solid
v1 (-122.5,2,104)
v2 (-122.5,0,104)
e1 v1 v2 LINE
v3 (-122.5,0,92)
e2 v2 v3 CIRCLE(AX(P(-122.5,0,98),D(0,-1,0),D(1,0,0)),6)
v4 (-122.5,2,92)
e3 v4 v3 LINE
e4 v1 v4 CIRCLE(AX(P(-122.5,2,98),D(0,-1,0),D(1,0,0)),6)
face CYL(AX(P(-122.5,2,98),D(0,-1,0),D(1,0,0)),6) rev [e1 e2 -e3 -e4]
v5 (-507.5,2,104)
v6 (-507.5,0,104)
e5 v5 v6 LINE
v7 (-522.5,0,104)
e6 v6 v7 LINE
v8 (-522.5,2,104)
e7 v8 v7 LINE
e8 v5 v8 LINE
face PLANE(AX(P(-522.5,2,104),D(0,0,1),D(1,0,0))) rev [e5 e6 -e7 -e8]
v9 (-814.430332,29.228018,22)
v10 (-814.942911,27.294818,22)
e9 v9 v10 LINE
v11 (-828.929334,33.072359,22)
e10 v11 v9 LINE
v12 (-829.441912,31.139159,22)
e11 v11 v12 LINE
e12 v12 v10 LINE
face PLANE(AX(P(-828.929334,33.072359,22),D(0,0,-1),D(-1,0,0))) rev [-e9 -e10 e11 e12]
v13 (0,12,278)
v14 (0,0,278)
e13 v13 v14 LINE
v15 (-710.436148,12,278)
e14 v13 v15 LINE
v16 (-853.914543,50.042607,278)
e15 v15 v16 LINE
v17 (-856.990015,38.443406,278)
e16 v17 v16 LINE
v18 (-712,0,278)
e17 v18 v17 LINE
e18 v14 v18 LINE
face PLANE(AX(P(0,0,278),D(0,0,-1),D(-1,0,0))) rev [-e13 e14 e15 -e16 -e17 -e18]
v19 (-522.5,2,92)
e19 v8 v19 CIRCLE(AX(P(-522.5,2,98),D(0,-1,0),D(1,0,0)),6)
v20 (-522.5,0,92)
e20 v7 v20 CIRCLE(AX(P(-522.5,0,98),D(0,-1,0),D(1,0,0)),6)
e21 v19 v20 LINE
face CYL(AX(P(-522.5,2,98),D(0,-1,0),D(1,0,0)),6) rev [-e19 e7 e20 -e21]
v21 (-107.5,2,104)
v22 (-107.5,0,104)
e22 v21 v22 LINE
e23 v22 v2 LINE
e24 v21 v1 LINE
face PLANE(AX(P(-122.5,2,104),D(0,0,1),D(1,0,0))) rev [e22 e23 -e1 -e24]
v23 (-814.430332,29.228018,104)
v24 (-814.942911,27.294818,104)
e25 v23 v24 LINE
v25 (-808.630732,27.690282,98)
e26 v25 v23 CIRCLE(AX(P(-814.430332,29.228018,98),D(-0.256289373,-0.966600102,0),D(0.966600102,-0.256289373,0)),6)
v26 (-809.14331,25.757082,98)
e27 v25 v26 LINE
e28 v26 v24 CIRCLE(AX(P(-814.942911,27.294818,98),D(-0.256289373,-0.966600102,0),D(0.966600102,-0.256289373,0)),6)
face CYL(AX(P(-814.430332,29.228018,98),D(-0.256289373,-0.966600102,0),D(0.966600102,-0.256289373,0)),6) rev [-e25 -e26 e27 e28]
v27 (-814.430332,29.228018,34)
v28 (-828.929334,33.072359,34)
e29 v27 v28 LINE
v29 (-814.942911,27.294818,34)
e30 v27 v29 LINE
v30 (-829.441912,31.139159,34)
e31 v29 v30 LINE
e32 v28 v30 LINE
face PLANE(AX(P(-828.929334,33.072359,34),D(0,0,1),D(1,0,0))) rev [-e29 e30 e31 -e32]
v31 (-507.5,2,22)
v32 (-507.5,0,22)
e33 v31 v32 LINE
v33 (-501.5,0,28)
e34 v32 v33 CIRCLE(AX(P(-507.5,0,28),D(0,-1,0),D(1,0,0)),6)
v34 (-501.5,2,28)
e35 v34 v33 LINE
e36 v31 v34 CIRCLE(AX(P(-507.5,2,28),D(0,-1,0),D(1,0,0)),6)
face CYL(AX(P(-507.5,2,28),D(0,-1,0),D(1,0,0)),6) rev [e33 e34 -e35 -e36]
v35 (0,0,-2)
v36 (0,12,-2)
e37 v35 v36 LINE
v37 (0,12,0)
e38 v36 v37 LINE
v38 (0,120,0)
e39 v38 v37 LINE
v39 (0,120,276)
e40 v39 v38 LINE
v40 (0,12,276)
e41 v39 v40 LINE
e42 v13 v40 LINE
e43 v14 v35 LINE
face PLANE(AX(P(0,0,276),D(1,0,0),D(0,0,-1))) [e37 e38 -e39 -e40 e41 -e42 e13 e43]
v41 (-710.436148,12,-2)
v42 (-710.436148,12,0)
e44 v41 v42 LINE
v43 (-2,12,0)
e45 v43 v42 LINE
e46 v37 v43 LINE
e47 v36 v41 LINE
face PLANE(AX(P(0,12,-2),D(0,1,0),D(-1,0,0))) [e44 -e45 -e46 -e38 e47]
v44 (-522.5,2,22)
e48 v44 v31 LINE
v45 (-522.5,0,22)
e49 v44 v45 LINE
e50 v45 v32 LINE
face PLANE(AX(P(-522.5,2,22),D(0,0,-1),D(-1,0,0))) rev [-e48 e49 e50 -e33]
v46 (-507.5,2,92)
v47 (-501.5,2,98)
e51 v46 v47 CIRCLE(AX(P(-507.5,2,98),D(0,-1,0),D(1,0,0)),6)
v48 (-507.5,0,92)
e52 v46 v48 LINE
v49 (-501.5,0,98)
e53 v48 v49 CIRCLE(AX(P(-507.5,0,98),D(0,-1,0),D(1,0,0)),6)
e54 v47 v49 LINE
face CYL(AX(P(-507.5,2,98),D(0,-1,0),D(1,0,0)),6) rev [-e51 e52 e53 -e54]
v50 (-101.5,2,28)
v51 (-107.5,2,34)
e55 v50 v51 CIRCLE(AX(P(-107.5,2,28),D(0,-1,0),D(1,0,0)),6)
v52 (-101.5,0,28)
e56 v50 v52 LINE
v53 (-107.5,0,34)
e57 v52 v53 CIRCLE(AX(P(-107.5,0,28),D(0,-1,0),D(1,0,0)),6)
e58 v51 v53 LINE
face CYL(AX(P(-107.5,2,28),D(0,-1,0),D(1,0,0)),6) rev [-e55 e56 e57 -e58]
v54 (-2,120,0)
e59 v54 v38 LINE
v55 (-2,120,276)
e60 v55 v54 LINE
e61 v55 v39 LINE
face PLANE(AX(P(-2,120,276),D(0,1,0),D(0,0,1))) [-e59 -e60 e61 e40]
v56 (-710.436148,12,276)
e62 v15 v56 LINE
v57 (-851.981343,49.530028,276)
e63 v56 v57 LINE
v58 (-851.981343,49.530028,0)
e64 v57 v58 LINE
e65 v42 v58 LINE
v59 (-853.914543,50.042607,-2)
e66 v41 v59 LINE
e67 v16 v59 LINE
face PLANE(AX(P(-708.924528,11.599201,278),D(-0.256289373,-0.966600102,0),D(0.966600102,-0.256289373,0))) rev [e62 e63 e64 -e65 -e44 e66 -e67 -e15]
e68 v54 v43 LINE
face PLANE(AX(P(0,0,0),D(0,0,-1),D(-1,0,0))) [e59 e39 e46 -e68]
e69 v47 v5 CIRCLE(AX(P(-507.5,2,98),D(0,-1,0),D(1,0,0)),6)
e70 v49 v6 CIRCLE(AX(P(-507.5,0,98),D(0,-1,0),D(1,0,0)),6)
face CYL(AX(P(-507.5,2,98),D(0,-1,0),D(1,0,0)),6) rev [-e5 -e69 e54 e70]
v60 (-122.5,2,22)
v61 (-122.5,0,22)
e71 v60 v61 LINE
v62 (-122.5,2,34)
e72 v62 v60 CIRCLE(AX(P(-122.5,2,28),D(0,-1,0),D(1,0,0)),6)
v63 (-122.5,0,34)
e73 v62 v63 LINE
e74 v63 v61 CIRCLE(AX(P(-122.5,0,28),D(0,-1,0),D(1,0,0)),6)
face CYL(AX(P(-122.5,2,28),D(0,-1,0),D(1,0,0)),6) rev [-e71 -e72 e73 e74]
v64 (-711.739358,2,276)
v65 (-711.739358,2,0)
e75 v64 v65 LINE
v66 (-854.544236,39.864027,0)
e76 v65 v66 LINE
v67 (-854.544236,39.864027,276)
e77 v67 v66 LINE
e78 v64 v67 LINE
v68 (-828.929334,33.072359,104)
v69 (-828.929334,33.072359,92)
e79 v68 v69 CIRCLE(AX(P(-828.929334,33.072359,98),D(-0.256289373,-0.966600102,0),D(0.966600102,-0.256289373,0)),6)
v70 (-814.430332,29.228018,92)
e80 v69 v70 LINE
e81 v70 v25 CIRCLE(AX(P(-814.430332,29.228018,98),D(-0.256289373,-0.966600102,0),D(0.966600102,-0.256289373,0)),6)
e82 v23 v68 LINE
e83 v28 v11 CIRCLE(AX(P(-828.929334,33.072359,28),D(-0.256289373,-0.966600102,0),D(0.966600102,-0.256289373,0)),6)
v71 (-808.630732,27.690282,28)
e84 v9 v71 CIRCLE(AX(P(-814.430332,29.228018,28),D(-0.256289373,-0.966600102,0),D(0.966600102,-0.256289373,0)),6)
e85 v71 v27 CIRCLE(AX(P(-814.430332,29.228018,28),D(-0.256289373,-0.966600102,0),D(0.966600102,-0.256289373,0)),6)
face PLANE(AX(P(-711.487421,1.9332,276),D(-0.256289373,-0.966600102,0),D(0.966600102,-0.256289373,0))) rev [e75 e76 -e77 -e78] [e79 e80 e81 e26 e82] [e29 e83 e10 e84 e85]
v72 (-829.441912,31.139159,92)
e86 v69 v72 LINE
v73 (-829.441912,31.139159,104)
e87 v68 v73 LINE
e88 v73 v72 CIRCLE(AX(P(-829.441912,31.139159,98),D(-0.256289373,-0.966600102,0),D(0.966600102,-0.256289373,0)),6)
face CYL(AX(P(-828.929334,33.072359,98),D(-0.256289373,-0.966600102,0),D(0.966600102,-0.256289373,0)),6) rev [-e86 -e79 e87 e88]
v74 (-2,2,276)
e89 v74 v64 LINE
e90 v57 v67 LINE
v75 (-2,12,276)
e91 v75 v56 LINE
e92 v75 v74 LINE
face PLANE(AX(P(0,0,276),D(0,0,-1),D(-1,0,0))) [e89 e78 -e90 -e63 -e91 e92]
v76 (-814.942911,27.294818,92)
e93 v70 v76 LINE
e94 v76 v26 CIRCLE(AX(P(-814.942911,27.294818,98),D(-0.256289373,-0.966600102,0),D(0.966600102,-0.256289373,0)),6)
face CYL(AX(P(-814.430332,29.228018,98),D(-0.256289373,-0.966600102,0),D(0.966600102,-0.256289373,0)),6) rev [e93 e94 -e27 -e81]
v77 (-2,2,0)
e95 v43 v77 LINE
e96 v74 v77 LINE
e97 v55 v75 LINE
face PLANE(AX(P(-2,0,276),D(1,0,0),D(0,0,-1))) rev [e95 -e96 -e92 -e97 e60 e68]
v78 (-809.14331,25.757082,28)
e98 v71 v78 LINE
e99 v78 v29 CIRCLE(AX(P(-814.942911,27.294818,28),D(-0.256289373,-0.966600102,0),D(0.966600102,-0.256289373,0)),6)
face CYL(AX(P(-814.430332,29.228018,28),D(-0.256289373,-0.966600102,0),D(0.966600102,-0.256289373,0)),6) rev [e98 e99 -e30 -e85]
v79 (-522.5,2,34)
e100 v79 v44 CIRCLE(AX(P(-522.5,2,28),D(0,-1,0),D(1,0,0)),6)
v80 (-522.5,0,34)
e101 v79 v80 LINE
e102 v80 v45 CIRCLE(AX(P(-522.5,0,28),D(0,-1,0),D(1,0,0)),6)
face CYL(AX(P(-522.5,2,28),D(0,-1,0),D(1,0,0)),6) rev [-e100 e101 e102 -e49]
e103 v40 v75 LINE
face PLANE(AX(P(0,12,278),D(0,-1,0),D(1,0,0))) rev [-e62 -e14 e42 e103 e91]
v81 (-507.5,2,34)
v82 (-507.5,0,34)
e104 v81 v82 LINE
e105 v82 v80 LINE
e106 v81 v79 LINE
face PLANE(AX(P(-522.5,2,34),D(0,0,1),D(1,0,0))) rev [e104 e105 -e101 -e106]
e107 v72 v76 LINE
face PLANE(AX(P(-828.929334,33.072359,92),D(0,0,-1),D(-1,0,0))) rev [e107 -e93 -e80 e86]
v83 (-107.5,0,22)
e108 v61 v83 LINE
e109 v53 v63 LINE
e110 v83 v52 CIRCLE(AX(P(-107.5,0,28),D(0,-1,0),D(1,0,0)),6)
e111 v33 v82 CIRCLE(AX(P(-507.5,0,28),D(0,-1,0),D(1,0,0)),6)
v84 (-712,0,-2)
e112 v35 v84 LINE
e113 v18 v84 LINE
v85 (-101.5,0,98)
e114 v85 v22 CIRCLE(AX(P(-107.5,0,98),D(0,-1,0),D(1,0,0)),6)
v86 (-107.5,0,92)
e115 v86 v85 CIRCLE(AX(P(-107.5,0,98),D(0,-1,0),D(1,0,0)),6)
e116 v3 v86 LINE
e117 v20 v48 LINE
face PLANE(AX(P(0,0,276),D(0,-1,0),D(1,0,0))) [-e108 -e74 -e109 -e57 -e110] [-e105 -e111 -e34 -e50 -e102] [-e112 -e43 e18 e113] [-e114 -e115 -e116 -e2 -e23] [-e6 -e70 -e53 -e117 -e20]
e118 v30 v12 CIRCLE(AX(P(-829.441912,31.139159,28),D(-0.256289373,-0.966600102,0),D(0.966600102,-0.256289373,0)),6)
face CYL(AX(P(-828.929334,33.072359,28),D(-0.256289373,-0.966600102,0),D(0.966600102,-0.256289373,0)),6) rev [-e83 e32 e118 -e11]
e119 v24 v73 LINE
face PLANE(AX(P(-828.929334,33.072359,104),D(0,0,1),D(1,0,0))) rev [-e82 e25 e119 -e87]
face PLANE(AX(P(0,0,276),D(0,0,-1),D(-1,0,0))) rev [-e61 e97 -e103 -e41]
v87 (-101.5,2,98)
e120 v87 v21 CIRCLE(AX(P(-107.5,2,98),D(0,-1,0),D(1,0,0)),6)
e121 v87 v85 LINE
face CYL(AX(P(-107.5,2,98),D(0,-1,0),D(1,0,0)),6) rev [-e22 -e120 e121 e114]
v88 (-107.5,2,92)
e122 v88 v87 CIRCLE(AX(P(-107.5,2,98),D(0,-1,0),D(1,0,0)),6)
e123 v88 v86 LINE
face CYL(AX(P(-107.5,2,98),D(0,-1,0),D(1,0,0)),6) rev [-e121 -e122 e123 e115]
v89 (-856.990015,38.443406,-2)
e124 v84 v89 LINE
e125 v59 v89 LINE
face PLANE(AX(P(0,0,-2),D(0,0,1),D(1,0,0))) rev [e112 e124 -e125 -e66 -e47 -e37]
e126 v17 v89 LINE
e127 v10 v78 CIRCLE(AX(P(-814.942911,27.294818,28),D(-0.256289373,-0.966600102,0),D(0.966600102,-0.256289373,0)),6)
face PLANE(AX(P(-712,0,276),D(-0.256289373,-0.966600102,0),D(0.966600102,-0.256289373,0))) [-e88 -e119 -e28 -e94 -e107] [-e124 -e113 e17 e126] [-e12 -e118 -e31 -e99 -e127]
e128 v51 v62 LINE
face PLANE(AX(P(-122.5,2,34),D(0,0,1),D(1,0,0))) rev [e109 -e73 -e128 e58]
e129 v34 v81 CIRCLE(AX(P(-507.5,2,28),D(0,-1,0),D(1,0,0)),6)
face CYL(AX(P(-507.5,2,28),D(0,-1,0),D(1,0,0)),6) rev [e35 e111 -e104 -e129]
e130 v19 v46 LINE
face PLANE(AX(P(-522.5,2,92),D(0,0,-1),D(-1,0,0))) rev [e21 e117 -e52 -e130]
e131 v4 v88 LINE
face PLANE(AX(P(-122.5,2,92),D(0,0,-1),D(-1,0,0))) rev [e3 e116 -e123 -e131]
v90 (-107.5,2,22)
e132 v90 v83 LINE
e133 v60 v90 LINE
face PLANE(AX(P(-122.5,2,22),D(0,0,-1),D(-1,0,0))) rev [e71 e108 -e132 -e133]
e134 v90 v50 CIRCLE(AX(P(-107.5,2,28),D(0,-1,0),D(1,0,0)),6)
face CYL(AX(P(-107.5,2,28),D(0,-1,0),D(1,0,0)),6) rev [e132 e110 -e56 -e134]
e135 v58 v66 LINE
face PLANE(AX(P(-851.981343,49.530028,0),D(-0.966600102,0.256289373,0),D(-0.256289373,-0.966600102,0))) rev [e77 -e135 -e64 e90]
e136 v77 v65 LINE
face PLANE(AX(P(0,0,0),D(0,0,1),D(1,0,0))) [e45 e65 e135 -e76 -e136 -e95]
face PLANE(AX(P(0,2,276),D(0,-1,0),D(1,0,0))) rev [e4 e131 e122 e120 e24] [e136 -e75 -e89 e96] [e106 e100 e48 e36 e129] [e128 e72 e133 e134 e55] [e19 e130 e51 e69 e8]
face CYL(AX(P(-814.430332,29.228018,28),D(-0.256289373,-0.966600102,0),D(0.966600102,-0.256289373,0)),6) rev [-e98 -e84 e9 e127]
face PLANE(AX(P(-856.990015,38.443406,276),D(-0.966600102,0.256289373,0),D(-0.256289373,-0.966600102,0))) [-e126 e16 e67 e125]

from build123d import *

# Parameters (mm, degrees)
EXTRUDE_THIN1_DEPTH  = 276
EXTRUDE_THIN2_DEPTH  = 2
EXTRUDE_THIN3_DEPTH  = 2
CUT_EXTRUDE1_DEPTH   = 2
CUT_EXTRUDE2_DEPTH   = 2
SKETCH7_W            = 2
SKETCH7_H            = 276
BOSS_EXTRUDE1_DEPTH  = 10
LPATTERN1_COUNT      = 2
LPATTERN1_PITCH      = 70
LPATTERN2_COUNT      = 2
LPATTERN2_PITCH      = 70
LPATTERN2_COUNT_DIR2 = 2
LPATTERN2_PITCH_DIR2 = 400


with BuildPart() as part:
    # Sketch1 → Extrude-Thin1 (new body)
    with BuildSketch(Plane.XY):
        Polygon((-856.990015303, 38.44340597), (-712, 0), (0, 0), (0, 120), (-2, 120), (-2, 2), (-711.739357917, 2), (-856.477436556, 40.376606174), align=None)
    extrude(amount=EXTRUDE_THIN1_DEPTH)

    # Sketch2 → Extrude-Thin2 (add)
    with BuildSketch(Plane.XY.offset(276)):
        Polygon((0, 0), (-712, 0), (-856.990015303, 38.44340597), (-853.914542825, 50.042607194), (-710.436147504, 12), (0, 12), align=None)
    extrude(amount=EXTRUDE_THIN2_DEPTH)

    # Sketch4 → Extrude-Thin3 (add)
    with BuildSketch(Plane(origin=(0, 0, 0), x_dir=(-1, 0, 0), z_dir=(0, 0, -1))):
        Polygon((0, 0), (712, 0), (856.990015303, 38.44340597), (853.914542825, 50.042607194), (710.436147504, 12), (0, 12), align=None)
    extrude(amount=EXTRUDE_THIN3_DEPTH)

    # Sketch5 → Cut-Extrude1 (cut)
    with BuildSketch(Plane.XZ):
        with BuildLine():
            Line((-122.5, 34), (-107.5, 34))
            ThreePointArc((-107.5, 34), (-101.5, 28), (-107.5, 22))
            Line((-107.5, 22), (-122.5, 22))
            ThreePointArc((-122.5, 22), (-128.5, 28), (-122.5, 34))
        make_face()
    cut_extrude1 = extrude(amount=-CUT_EXTRUDE1_DEPTH, mode=Mode.SUBTRACT)

    # Sketch6 → Cut-Extrude2 (cut)
    with BuildSketch(Plane(origin=(-46.76718086, -176.383285962, 0), x_dir=(0.9666001020169073, -0.2562893731329973, 0), z_dir=(-0.2562893731329973, -0.9666001020169073, 0))):
        with BuildLine():
            Line((-809.719272636, 34), (-794.719272636, 34))
            ThreePointArc((-794.719272636, 34), (-788.719272636, 28), (-794.719272636, 22))
            Line((-794.719272636, 22), (-809.719272636, 22))
            ThreePointArc((-809.719272636, 22), (-815.719272636, 28), (-809.719272636, 34))
        make_face()
    cut_extrude2 = extrude(amount=-CUT_EXTRUDE2_DEPTH, mode=Mode.SUBTRACT)

    # Sketch7 → Boss-Extrude1 (add)
    with BuildSketch(Plane(origin=(-46.254602114, -174.450085758, 0), x_dir=(0.9666001020169073, -0.25628937313299727, 0), z_dir=(0.25628937313299727, 0.9666001020169073, 0))):
        with Locations((-837.219272636, -138)):
            Rectangle(SKETCH7_W, SKETCH7_H)
    extrude(amount=BOSS_EXTRUDE1_DEPTH)

    # LPattern1: Cut-Extrude2 ×2
    with Locations(*[(0, 0, i * LPATTERN1_PITCH) for i in range(1, LPATTERN1_COUNT)]):
        add(cut_extrude2, mode=Mode.SUBTRACT)

    # LPattern2: Cut-Extrude1 2 × 2
    with Locations(*[(-j * LPATTERN2_PITCH_DIR2, 0, i * LPATTERN2_PITCH) for i in range(LPATTERN2_COUNT) for j in range(LPATTERN2_COUNT_DIR2) if (i, j) != (0, 0)]):
        add(cut_extrude1, mode=Mode.SUBTRACT)


solid = part.part
